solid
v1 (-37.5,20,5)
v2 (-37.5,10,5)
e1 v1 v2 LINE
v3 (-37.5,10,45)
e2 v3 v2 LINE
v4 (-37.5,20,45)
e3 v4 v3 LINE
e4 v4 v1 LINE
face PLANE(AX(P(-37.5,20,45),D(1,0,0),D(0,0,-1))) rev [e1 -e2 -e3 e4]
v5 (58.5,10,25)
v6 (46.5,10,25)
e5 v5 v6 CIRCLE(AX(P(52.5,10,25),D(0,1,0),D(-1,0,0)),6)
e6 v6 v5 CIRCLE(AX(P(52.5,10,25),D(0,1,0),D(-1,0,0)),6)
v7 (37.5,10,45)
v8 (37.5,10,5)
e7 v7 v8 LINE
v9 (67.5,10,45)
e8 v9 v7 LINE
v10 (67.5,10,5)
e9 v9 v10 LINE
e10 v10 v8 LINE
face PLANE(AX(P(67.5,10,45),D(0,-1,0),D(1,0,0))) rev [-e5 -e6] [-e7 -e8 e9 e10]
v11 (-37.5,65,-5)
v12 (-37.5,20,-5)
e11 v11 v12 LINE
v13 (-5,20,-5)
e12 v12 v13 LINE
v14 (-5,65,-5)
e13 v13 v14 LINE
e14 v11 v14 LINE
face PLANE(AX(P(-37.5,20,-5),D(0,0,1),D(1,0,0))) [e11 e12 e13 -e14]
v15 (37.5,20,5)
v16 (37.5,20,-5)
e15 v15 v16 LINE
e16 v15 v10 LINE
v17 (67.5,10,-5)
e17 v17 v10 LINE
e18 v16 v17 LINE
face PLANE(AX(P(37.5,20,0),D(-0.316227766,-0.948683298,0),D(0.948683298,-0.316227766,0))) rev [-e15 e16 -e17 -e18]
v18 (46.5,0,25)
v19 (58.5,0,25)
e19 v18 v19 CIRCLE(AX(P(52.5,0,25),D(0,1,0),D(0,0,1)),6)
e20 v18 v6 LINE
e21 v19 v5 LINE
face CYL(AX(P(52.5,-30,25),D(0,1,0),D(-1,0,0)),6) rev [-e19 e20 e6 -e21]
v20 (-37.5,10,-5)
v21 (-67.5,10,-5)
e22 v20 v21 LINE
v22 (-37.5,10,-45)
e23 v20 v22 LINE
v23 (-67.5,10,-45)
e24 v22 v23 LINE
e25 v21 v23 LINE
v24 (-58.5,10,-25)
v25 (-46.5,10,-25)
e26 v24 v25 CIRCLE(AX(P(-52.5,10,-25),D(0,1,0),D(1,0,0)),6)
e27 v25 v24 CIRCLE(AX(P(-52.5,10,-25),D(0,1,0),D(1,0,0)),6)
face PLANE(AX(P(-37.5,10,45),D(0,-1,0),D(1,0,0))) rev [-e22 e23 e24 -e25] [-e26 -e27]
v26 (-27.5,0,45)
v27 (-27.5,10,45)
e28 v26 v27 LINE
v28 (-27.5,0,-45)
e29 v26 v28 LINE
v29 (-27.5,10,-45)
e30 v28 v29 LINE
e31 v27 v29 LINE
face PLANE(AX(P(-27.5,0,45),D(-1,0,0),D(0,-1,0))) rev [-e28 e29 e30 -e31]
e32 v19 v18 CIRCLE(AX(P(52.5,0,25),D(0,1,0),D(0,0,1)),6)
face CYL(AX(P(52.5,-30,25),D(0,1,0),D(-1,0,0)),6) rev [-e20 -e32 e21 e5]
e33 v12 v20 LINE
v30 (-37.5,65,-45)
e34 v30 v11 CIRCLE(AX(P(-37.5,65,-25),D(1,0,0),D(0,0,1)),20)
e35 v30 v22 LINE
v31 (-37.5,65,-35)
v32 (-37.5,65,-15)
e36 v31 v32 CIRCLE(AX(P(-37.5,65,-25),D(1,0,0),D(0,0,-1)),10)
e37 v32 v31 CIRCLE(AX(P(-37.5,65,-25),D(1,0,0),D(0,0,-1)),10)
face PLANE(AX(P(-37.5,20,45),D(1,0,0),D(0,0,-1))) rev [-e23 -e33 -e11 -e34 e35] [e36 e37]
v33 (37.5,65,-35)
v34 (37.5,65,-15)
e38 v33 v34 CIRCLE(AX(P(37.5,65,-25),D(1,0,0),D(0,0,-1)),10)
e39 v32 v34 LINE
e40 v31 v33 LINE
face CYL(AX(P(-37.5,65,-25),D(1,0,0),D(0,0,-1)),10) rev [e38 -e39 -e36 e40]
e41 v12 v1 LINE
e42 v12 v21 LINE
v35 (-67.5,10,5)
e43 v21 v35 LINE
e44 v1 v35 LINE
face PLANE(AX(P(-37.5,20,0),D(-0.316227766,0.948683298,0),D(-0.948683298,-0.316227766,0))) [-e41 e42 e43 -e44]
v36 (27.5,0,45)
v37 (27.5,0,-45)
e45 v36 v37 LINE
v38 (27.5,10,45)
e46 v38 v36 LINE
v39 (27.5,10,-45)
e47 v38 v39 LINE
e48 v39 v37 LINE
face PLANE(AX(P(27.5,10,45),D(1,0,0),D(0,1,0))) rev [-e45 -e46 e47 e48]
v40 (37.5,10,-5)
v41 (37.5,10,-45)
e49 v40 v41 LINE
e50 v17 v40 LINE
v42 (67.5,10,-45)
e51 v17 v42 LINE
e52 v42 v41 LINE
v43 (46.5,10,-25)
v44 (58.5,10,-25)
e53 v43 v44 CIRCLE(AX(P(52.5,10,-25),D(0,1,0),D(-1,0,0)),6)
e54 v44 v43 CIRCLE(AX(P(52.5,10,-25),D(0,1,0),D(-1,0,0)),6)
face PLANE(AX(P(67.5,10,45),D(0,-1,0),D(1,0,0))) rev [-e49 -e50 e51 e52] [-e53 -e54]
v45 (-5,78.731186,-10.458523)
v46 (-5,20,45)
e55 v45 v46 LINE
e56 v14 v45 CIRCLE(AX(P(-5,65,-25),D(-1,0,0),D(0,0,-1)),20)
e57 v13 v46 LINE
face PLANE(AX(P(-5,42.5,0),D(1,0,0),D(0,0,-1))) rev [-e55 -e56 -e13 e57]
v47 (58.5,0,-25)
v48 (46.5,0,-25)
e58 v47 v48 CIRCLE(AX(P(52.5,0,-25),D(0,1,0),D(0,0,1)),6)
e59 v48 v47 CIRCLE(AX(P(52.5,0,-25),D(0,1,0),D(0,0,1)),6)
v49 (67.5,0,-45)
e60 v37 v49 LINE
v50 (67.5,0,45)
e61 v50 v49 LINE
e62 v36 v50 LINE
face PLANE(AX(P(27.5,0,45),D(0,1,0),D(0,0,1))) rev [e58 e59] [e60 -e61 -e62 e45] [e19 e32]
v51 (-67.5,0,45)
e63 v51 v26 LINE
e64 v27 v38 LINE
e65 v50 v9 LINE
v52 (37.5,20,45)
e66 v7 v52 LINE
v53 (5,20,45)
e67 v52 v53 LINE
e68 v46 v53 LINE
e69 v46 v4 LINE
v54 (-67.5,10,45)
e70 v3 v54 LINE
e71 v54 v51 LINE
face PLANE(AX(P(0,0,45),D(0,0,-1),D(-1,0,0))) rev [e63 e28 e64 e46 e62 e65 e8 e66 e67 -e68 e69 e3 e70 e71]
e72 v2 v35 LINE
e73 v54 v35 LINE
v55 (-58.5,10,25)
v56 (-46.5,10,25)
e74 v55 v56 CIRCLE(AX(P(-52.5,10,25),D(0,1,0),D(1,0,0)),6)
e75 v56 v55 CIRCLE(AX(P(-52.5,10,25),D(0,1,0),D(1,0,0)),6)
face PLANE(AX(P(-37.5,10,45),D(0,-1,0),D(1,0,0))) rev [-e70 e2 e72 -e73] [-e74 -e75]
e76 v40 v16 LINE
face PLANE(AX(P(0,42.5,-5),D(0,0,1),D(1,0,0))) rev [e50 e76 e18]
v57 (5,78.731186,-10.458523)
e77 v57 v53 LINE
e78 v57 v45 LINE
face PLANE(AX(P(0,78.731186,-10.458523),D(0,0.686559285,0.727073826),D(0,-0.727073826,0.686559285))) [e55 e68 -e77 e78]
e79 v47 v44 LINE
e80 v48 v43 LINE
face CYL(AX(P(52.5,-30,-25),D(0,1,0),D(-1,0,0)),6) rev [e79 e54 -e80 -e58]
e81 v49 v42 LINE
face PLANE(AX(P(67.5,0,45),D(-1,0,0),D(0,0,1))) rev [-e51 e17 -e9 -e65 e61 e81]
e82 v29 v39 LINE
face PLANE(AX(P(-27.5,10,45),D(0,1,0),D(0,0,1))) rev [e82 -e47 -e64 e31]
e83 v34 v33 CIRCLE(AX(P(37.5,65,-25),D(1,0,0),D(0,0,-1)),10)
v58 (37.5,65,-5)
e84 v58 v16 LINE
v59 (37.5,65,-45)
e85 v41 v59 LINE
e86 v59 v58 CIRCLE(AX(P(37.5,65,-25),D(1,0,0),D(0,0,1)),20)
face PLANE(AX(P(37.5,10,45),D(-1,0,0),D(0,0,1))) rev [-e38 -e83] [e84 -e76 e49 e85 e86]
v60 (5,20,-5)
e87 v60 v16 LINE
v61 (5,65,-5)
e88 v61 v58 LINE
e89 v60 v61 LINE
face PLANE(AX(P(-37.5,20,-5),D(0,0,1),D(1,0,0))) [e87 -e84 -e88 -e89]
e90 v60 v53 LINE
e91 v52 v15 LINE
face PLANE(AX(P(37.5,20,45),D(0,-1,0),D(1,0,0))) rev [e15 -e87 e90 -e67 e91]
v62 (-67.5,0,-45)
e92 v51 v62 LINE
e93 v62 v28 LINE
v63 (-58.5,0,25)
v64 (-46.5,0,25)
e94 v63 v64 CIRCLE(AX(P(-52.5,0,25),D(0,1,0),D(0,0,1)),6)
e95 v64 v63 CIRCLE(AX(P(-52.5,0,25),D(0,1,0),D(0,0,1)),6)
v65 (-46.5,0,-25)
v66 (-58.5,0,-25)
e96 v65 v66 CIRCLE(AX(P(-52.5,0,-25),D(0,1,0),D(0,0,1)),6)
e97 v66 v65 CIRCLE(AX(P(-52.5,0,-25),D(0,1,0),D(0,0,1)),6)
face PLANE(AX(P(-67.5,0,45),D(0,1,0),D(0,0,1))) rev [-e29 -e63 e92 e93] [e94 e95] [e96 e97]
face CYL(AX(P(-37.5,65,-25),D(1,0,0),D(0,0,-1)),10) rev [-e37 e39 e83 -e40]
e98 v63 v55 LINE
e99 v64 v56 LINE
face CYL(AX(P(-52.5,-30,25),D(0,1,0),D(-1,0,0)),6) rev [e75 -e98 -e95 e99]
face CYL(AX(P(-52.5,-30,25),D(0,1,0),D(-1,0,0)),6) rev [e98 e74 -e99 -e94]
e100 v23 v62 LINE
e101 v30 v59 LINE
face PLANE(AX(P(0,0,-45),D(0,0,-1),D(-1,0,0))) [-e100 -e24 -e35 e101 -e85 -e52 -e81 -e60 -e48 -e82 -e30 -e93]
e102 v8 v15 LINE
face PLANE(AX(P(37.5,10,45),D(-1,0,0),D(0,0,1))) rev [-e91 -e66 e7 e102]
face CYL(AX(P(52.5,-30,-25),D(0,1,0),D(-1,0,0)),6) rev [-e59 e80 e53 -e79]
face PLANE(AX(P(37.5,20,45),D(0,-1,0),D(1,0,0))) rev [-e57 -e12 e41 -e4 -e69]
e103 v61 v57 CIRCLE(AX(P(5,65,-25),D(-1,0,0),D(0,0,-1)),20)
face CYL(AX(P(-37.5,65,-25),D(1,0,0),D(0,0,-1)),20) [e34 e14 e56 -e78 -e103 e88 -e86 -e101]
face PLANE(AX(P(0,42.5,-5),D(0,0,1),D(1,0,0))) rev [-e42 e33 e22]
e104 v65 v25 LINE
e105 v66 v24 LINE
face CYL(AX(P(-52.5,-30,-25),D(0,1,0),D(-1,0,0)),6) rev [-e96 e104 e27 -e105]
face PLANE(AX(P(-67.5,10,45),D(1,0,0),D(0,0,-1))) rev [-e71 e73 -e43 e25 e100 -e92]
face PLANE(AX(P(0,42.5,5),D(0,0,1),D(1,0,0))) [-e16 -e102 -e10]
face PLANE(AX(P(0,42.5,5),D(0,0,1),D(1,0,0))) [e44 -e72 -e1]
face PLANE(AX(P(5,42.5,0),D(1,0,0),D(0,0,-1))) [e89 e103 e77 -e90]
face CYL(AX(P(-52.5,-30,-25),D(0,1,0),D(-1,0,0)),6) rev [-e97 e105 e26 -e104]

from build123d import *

# Parameters (mm, degrees)
BASE_PLATE_DEPTH            = 45
MOUNTING_HOLES_SKETCH_R     = 6
MOUNTING_HOLES_DEPTH        = 40
PIVOT_BOSS_PROFILE_R        = 10
PIVOT_BOSS_DEPTH            = 75
CENTER_GUSSET_RIB_REACH     = 119.5
CENTER_GUSSET_SKETCH_WALL_W = 317.777472108
CENTER_GUSSET_SKETCH_WALL_H = 10
SIDE_GUSSET_RIB_REACH       = 119.5
SIDE_GUSSET_SKETCH_WALL_W   = 268.622776602
SIDE_GUSSET_SKETCH_WALL_H   = 10


with BuildPart() as part:
    # Base Plate Profile → Base Plate (new, symmetric)
    with BuildSketch(Plane.XY):
        Polygon((-67.5, 0), (-27.5, 0), (-27.5, 10), (27.5, 10), (27.5, 0), (67.5, 0), (67.5, 10), (37.5, 10), (37.5, 20), (-37.5, 20), (-37.5, 10), (-67.5, 10), align=None)
    extrude(amount=BASE_PLATE_DEPTH, both=True)

    # Mounting Holes Sketch → Mounting Holes (cut)
    with BuildSketch(Plane(origin=(0, 10, 0), x_dir=(1, 0, 0), z_dir=(0, 1, 0))):
        with Locations(Location((52.5, -25, 0), (0, 0, 180))):
            Circle(MOUNTING_HOLES_SKETCH_R)
        with Locations(Location((52.5, 25, 0), (0, 0, 180))):
            Circle(MOUNTING_HOLES_SKETCH_R)
        with Locations(Location((-52.5, 25, 0), (0, 0, 270))):
            Circle(MOUNTING_HOLES_SKETCH_R)
        with Locations(Location((-52.5, -25, 0), (0, 0, 270))):
            Circle(MOUNTING_HOLES_SKETCH_R)
    extrude(amount=-MOUNTING_HOLES_DEPTH, mode=Mode.SUBTRACT)

    # Pivot Boss Profile → Pivot Boss (add)
    with BuildSketch(Plane(origin=(37.5, 0, 0), x_dir=(0, 0, -1), z_dir=(1, 0, 0))):
        with BuildLine():
            Line((45, 20), (5, 20))
            Line((5, 20), (5, 65))
            ThreePointArc((5, 65), (25, 85), (45, 65))
            Line((45, 65), (45, 20))
        make_face()
        with Locations((25, 65)):
            Circle(PIVOT_BOSS_PROFILE_R, mode=Mode.SUBTRACT)
    extrude(amount=-PIVOT_BOSS_DEPTH)

    # Center Gusset Sketch wall → Center Gusset Rib (add, up to next)
    with BuildSketch(Plane(origin=(0, 49.365592849, 17.270738259), x_dir=(0, -0.727073825966, 0.686559284837), z_dir=(0, -0.686559284837, -0.727073825966)), mode=Mode.PRIVATE) as center_gusset_rib_sk1:
        Rectangle(CENTER_GUSSET_SKETCH_WALL_W, CENTER_GUSSET_SKETCH_WALL_H)
    center_gusset_rib_tool1 = extrude(center_gusset_rib_sk1.sketch, amount=CENTER_GUSSET_RIB_REACH, mode=Mode.PRIVATE) - part.part
    add(center_gusset_rib_tool1.solids().sort_by_distance((0, 49.365592849, 17.270738259))[0])

    # Side Gusset Sketch wall → Side Gusset Rib (add, up to next)
    with BuildSketch(Plane(origin=(-52.5, 15, 0), x_dir=(-0.948683298051, -0.316227766017, 0), z_dir=(0.316227766017, -0.948683298051, 0)), mode=Mode.PRIVATE) as side_gusset_rib_sk1:
        Rectangle(SIDE_GUSSET_SKETCH_WALL_W, SIDE_GUSSET_SKETCH_WALL_H)
    side_gusset_rib_tool1 = extrude(side_gusset_rib_sk1.sketch, amount=SIDE_GUSSET_RIB_REACH, mode=Mode.PRIVATE) - part.part
    side_gusset_rib = side_gusset_rib_tool1.solids().sort_by_distance((-52.5, 15, 0))[0]
    add(side_gusset_rib)

    # Side Gusset Mirror: Side Gusset Rib across plane
    add(side_gusset_rib.mirror(Plane(origin=(0, 0, 0), x_dir=(0, 0, 1), z_dir=(1, 0, 0))))


solid = part.part
